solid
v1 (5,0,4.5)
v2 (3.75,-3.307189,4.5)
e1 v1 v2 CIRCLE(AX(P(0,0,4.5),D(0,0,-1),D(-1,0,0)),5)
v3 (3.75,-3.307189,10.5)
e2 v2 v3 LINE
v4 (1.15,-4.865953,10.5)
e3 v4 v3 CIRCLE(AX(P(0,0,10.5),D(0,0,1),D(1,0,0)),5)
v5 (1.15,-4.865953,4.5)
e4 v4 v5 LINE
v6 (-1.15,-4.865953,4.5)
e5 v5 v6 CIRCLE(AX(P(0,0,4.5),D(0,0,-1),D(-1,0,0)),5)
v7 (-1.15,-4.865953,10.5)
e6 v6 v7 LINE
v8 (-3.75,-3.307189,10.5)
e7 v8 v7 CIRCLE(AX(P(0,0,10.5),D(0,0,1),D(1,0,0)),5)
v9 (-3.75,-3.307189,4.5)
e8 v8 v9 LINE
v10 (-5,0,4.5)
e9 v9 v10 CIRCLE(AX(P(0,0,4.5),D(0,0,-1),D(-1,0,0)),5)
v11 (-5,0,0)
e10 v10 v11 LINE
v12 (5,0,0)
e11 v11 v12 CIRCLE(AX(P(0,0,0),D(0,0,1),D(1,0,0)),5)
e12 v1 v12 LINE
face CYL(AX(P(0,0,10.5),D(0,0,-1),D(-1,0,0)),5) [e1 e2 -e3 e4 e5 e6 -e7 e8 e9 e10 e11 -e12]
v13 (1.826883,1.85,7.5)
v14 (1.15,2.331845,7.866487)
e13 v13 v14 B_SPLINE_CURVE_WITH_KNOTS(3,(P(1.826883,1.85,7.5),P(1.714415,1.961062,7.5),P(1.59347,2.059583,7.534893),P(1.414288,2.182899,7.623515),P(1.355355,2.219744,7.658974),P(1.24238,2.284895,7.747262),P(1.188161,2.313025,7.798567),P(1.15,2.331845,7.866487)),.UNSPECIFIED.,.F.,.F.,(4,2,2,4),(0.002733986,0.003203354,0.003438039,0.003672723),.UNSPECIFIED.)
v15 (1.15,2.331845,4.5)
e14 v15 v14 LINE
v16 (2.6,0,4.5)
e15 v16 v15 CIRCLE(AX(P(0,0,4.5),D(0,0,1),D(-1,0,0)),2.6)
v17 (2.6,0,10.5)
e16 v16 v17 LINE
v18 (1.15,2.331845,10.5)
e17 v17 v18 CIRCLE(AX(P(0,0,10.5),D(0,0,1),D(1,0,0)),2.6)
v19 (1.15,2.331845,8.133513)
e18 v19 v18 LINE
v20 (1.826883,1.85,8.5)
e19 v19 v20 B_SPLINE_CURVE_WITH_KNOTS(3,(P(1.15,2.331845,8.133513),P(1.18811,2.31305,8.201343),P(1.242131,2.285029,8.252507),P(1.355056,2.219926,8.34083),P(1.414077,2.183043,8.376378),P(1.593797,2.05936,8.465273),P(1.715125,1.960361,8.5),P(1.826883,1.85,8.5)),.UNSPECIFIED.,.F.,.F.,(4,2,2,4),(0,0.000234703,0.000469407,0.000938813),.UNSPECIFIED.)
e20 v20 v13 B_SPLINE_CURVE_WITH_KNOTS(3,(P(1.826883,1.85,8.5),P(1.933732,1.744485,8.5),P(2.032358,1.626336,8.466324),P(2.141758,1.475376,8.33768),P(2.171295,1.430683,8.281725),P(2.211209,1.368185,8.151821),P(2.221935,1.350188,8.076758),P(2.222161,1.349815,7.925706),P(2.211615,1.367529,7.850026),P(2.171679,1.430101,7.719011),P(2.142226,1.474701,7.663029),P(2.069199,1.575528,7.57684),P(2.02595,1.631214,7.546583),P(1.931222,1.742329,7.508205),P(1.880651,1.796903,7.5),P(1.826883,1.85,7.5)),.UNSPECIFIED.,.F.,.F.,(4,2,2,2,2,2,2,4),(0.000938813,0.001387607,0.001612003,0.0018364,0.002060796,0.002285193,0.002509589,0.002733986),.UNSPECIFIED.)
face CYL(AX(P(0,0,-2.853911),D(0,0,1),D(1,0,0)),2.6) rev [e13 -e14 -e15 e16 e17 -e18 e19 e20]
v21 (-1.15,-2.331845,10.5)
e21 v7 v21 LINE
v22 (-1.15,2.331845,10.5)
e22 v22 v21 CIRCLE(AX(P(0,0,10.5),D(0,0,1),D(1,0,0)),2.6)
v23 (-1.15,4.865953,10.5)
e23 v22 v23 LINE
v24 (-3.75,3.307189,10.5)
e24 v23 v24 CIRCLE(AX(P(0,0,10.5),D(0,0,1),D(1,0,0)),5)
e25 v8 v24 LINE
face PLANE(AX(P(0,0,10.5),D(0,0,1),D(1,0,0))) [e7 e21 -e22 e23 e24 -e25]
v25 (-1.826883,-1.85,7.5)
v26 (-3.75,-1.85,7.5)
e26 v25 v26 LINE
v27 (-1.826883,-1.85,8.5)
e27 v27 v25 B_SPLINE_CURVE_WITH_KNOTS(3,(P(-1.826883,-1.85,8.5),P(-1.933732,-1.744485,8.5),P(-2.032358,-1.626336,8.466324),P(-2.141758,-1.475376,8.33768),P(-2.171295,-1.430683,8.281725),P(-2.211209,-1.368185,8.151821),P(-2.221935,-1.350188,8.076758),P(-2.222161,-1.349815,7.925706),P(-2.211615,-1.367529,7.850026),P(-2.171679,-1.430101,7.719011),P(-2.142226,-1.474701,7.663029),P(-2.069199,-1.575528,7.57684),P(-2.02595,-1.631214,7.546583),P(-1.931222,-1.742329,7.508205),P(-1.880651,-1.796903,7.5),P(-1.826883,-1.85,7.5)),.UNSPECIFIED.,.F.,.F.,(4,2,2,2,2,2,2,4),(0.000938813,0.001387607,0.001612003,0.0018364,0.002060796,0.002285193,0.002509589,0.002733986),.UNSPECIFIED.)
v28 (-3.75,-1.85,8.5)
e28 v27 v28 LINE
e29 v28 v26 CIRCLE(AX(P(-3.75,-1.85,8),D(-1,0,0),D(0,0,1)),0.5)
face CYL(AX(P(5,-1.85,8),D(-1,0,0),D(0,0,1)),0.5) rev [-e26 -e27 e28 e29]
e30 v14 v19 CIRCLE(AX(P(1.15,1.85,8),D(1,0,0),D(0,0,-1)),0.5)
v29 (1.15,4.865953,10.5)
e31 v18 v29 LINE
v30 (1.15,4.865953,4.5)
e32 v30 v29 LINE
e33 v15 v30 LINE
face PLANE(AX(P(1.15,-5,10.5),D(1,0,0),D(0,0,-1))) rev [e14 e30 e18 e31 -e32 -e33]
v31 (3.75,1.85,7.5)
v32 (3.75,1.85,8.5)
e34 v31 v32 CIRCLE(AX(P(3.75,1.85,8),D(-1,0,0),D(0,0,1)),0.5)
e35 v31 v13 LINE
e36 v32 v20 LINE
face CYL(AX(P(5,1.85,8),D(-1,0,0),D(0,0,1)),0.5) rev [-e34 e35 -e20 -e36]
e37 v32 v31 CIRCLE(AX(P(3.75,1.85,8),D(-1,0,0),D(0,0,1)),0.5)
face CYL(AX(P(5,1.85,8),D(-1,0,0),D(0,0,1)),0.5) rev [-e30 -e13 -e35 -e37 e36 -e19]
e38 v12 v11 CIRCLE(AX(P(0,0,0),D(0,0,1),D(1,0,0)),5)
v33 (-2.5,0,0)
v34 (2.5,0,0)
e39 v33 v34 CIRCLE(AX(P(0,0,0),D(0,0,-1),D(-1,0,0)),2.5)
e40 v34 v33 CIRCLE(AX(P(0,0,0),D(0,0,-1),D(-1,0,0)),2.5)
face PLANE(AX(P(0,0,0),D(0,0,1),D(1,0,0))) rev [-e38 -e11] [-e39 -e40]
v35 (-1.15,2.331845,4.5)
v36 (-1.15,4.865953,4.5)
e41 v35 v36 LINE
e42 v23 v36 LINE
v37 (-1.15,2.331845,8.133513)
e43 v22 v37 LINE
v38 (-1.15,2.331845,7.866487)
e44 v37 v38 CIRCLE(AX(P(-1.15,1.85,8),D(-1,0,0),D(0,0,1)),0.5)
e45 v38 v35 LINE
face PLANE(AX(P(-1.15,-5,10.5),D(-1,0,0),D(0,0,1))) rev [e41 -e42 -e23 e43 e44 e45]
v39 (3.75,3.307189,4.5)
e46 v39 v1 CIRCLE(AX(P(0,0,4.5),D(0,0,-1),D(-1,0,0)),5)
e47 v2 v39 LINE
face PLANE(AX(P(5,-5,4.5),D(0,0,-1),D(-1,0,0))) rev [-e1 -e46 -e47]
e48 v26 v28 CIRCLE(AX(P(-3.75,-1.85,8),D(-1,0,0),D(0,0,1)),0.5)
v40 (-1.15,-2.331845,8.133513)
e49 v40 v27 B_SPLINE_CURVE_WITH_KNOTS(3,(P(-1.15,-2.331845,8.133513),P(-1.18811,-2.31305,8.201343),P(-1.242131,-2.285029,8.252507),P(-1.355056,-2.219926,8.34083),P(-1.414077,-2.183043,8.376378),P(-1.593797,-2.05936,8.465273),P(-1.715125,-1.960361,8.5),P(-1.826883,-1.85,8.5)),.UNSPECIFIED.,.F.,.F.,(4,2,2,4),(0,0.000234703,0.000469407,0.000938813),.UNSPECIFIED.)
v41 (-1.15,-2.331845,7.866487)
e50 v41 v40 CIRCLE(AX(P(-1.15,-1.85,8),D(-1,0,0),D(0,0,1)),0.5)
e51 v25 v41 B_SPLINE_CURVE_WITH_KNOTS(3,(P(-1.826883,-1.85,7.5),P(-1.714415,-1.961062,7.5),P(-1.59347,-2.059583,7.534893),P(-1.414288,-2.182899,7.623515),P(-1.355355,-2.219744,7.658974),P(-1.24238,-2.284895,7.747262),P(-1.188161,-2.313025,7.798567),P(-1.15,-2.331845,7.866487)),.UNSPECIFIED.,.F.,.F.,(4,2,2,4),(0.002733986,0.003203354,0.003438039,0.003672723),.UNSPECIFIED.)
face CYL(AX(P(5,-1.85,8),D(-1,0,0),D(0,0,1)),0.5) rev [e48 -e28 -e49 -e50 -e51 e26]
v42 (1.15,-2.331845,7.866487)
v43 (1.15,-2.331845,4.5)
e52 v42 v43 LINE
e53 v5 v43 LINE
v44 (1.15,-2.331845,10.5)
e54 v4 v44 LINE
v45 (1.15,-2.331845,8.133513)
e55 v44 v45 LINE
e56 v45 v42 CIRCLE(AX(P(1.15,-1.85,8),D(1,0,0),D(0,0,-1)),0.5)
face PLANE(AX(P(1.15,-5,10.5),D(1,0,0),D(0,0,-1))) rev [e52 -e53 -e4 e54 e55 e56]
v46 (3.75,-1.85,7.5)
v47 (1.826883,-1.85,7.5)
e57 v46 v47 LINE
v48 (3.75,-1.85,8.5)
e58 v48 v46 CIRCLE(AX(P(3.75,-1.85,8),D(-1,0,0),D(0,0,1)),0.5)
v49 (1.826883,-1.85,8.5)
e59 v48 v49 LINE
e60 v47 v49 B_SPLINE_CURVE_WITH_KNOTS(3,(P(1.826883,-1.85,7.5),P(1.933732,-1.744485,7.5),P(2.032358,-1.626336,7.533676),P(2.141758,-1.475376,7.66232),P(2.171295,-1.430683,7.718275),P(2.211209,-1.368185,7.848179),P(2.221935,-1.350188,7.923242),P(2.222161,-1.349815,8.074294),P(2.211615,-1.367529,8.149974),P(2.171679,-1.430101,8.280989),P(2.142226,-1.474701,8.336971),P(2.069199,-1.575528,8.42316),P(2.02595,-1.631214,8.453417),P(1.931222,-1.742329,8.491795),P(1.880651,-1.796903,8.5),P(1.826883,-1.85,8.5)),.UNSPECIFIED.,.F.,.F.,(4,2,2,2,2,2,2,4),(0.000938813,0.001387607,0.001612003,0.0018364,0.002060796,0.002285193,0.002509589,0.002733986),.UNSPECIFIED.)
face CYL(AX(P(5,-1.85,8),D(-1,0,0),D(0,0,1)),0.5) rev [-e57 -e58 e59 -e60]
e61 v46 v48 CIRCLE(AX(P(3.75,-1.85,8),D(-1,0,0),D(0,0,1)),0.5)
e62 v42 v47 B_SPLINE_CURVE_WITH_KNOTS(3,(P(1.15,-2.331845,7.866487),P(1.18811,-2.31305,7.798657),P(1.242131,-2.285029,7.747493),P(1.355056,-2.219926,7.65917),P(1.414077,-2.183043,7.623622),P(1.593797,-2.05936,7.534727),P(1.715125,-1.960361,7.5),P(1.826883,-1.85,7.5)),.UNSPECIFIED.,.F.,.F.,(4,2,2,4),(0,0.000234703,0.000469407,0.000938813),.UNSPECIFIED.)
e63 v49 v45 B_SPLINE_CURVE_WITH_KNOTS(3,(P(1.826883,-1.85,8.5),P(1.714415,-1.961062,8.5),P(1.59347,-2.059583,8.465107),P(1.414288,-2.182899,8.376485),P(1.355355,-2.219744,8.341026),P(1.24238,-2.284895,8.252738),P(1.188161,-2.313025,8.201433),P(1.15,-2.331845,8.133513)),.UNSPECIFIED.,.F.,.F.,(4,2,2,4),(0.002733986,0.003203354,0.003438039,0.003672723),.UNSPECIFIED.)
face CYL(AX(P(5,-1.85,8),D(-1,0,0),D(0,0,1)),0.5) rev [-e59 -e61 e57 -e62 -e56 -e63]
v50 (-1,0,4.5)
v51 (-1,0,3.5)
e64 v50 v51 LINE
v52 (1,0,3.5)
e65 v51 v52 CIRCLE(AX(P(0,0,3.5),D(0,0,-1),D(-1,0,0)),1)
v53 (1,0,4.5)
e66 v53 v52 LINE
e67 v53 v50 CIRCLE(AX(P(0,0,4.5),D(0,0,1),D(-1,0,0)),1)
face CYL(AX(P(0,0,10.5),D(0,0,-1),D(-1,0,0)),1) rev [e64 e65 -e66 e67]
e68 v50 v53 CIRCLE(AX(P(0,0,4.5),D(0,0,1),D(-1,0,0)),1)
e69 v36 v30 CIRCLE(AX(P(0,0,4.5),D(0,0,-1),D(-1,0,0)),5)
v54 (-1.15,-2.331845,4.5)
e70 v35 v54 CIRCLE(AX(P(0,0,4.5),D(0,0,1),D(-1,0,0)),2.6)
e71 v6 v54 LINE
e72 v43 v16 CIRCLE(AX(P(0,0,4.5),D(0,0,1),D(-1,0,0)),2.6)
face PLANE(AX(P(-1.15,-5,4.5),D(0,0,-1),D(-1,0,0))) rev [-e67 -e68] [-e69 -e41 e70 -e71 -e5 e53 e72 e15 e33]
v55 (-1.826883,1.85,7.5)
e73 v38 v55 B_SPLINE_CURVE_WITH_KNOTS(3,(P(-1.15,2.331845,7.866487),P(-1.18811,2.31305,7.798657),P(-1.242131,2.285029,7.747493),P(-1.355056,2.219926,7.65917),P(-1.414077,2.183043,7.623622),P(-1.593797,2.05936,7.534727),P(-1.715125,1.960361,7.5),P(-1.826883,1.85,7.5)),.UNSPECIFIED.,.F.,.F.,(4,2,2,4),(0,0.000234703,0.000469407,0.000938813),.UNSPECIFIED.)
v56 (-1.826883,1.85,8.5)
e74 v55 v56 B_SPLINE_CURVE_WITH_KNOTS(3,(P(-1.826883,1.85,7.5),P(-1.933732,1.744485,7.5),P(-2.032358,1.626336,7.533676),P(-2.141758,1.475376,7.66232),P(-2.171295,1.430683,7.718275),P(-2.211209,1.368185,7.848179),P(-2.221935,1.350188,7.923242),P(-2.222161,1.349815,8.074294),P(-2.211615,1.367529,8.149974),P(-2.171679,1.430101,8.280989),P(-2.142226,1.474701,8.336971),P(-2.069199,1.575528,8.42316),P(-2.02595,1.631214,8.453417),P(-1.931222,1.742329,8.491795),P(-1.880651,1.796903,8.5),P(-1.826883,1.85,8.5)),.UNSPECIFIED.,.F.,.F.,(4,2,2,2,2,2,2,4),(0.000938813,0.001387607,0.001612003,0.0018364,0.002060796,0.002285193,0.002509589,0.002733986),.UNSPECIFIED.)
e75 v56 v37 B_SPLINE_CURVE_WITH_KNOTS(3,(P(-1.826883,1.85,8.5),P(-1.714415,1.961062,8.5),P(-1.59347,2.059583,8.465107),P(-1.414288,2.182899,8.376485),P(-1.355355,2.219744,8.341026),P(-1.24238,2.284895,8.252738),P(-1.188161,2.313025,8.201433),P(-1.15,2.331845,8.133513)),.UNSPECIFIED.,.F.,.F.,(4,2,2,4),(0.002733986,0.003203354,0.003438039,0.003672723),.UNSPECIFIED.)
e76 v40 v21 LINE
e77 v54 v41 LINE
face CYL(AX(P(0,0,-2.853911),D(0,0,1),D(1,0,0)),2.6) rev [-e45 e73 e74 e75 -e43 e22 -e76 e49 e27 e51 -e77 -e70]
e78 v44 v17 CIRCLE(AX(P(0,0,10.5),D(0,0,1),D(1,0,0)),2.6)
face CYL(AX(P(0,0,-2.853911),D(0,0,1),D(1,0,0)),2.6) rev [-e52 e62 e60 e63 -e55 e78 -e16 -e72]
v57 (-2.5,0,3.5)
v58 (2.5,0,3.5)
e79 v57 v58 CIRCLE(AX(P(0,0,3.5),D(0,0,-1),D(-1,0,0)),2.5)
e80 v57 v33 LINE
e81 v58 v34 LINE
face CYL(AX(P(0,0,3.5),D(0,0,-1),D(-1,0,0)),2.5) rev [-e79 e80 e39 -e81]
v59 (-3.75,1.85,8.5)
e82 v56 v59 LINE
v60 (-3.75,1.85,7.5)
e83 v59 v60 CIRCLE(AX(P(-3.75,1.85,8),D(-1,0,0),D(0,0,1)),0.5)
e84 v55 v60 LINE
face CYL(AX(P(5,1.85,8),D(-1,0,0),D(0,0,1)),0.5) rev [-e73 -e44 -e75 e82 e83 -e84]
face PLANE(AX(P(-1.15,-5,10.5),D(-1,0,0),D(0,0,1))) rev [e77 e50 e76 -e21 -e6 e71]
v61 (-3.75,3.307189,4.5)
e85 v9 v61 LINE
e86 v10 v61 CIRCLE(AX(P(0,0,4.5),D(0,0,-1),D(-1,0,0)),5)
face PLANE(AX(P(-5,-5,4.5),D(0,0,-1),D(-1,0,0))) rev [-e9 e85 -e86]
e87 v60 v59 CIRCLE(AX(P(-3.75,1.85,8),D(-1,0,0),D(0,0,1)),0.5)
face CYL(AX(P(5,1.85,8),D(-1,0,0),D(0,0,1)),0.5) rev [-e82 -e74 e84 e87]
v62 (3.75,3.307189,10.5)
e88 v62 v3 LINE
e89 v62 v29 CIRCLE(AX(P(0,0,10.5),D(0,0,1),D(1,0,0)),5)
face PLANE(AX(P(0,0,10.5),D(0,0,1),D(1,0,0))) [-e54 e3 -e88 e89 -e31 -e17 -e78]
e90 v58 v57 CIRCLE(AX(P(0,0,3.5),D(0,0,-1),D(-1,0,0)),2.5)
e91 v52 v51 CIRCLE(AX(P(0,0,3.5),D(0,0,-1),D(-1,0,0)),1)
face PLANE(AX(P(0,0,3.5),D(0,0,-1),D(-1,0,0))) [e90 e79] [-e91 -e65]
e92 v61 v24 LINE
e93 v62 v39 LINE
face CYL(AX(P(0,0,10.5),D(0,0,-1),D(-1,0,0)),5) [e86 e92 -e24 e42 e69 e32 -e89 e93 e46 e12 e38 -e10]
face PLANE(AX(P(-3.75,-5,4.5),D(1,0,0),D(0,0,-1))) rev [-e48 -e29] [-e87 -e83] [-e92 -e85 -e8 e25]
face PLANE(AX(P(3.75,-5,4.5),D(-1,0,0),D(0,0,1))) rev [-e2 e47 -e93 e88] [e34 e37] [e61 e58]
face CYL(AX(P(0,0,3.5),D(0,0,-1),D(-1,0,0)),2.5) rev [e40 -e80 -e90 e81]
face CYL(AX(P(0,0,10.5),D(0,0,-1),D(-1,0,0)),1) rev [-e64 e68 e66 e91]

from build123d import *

# Parameters (mm, degrees)
SKETCH2_R           = 5
BOSS_EXTRUDE1_DEPTH = 10.5
SKETCH3_R           = 2.5
CUT_EXTRUDE1_DEPTH  = 3.5
SKETCH4_R           = 1
CUT_EXTRUDE2_DEPTH  = 10.949874371
SKETCH5_W           = 1.25
SKETCH5_H           = 6
CUT_EXTRUDE3_DEPTH  = 16.33786165
SKETCH6_W           = 2.3
SKETCH6_H           = 6
CUT_EXTRUDE4_DEPTH  = 16.33786165
SKETCH7_R           = 2.6
CUT_EXTRUDE5_DEPTH  = 6
SKETCH8_R           = 0.5
CUT_EXTRUDE6_DEPTH  = 15.553779578


with BuildPart() as part:
    # Sketch2 → Boss-Extrude1 (new body)
    with BuildSketch(Plane.XY):
        with Locations(Location((0, 0, 0), (0, 0, 180))):
            Circle(SKETCH2_R)
    extrude(amount=BOSS_EXTRUDE1_DEPTH)

    # Sketch3 → Cut-Extrude1 (cut)
    with BuildSketch(Plane(origin=(0, 0, 0), x_dir=(-1, 0, 0), z_dir=(0, 0, -1))):
        Circle(SKETCH3_R)
    extrude(amount=-CUT_EXTRUDE1_DEPTH, mode=Mode.SUBTRACT)

    # Sketch4 → Cut-Extrude2 (cut, through all)
    with BuildSketch(Plane(origin=(0, 0, 3.5), x_dir=(-1, 0, 0), z_dir=(0, 0, -1))):
        Circle(SKETCH4_R)
    extrude(amount=-CUT_EXTRUDE2_DEPTH, mode=Mode.SUBTRACT)

    # Sketch5 → Cut-Extrude3 (cut, through all)
    with BuildSketch(Plane(origin=(0, 5, 0), x_dir=(1, 0, 0), z_dir=(0, 1, 0))):
        with Locations((-4.375, -7.5)):
            Rectangle(SKETCH5_W, SKETCH5_H)
        with Locations((4.375, -7.5)):
            Rectangle(SKETCH5_W, SKETCH5_H)
    extrude(amount=-CUT_EXTRUDE3_DEPTH, mode=Mode.SUBTRACT)

    # Sketch6 → Cut-Extrude4 (cut, through all)
    with BuildSketch(Plane(origin=(0, 5, 0), x_dir=(1, 0, 0), z_dir=(0, 1, 0))):
        with Locations((0, -7.5)):
            Rectangle(SKETCH6_W, SKETCH6_H)
    extrude(amount=-CUT_EXTRUDE4_DEPTH, mode=Mode.SUBTRACT)

    # Sketch7 → Cut-Extrude5 (cut)
    with BuildSketch(Plane.XY.offset(10.5)):
        Circle(SKETCH7_R)
    extrude(amount=-CUT_EXTRUDE5_DEPTH, mode=Mode.SUBTRACT)

    # Sketch8 → Cut-Extrude6 (cut, through all)
    with BuildSketch(Plane.ZY.offset(3.75)):
        with Locations((8, 1.85)):
            Circle(SKETCH8_R)
        with Locations((8, -1.85)):
            Circle(SKETCH8_R)
    extrude(amount=-CUT_EXTRUDE6_DEPTH, mode=Mode.SUBTRACT)


solid = part.part
